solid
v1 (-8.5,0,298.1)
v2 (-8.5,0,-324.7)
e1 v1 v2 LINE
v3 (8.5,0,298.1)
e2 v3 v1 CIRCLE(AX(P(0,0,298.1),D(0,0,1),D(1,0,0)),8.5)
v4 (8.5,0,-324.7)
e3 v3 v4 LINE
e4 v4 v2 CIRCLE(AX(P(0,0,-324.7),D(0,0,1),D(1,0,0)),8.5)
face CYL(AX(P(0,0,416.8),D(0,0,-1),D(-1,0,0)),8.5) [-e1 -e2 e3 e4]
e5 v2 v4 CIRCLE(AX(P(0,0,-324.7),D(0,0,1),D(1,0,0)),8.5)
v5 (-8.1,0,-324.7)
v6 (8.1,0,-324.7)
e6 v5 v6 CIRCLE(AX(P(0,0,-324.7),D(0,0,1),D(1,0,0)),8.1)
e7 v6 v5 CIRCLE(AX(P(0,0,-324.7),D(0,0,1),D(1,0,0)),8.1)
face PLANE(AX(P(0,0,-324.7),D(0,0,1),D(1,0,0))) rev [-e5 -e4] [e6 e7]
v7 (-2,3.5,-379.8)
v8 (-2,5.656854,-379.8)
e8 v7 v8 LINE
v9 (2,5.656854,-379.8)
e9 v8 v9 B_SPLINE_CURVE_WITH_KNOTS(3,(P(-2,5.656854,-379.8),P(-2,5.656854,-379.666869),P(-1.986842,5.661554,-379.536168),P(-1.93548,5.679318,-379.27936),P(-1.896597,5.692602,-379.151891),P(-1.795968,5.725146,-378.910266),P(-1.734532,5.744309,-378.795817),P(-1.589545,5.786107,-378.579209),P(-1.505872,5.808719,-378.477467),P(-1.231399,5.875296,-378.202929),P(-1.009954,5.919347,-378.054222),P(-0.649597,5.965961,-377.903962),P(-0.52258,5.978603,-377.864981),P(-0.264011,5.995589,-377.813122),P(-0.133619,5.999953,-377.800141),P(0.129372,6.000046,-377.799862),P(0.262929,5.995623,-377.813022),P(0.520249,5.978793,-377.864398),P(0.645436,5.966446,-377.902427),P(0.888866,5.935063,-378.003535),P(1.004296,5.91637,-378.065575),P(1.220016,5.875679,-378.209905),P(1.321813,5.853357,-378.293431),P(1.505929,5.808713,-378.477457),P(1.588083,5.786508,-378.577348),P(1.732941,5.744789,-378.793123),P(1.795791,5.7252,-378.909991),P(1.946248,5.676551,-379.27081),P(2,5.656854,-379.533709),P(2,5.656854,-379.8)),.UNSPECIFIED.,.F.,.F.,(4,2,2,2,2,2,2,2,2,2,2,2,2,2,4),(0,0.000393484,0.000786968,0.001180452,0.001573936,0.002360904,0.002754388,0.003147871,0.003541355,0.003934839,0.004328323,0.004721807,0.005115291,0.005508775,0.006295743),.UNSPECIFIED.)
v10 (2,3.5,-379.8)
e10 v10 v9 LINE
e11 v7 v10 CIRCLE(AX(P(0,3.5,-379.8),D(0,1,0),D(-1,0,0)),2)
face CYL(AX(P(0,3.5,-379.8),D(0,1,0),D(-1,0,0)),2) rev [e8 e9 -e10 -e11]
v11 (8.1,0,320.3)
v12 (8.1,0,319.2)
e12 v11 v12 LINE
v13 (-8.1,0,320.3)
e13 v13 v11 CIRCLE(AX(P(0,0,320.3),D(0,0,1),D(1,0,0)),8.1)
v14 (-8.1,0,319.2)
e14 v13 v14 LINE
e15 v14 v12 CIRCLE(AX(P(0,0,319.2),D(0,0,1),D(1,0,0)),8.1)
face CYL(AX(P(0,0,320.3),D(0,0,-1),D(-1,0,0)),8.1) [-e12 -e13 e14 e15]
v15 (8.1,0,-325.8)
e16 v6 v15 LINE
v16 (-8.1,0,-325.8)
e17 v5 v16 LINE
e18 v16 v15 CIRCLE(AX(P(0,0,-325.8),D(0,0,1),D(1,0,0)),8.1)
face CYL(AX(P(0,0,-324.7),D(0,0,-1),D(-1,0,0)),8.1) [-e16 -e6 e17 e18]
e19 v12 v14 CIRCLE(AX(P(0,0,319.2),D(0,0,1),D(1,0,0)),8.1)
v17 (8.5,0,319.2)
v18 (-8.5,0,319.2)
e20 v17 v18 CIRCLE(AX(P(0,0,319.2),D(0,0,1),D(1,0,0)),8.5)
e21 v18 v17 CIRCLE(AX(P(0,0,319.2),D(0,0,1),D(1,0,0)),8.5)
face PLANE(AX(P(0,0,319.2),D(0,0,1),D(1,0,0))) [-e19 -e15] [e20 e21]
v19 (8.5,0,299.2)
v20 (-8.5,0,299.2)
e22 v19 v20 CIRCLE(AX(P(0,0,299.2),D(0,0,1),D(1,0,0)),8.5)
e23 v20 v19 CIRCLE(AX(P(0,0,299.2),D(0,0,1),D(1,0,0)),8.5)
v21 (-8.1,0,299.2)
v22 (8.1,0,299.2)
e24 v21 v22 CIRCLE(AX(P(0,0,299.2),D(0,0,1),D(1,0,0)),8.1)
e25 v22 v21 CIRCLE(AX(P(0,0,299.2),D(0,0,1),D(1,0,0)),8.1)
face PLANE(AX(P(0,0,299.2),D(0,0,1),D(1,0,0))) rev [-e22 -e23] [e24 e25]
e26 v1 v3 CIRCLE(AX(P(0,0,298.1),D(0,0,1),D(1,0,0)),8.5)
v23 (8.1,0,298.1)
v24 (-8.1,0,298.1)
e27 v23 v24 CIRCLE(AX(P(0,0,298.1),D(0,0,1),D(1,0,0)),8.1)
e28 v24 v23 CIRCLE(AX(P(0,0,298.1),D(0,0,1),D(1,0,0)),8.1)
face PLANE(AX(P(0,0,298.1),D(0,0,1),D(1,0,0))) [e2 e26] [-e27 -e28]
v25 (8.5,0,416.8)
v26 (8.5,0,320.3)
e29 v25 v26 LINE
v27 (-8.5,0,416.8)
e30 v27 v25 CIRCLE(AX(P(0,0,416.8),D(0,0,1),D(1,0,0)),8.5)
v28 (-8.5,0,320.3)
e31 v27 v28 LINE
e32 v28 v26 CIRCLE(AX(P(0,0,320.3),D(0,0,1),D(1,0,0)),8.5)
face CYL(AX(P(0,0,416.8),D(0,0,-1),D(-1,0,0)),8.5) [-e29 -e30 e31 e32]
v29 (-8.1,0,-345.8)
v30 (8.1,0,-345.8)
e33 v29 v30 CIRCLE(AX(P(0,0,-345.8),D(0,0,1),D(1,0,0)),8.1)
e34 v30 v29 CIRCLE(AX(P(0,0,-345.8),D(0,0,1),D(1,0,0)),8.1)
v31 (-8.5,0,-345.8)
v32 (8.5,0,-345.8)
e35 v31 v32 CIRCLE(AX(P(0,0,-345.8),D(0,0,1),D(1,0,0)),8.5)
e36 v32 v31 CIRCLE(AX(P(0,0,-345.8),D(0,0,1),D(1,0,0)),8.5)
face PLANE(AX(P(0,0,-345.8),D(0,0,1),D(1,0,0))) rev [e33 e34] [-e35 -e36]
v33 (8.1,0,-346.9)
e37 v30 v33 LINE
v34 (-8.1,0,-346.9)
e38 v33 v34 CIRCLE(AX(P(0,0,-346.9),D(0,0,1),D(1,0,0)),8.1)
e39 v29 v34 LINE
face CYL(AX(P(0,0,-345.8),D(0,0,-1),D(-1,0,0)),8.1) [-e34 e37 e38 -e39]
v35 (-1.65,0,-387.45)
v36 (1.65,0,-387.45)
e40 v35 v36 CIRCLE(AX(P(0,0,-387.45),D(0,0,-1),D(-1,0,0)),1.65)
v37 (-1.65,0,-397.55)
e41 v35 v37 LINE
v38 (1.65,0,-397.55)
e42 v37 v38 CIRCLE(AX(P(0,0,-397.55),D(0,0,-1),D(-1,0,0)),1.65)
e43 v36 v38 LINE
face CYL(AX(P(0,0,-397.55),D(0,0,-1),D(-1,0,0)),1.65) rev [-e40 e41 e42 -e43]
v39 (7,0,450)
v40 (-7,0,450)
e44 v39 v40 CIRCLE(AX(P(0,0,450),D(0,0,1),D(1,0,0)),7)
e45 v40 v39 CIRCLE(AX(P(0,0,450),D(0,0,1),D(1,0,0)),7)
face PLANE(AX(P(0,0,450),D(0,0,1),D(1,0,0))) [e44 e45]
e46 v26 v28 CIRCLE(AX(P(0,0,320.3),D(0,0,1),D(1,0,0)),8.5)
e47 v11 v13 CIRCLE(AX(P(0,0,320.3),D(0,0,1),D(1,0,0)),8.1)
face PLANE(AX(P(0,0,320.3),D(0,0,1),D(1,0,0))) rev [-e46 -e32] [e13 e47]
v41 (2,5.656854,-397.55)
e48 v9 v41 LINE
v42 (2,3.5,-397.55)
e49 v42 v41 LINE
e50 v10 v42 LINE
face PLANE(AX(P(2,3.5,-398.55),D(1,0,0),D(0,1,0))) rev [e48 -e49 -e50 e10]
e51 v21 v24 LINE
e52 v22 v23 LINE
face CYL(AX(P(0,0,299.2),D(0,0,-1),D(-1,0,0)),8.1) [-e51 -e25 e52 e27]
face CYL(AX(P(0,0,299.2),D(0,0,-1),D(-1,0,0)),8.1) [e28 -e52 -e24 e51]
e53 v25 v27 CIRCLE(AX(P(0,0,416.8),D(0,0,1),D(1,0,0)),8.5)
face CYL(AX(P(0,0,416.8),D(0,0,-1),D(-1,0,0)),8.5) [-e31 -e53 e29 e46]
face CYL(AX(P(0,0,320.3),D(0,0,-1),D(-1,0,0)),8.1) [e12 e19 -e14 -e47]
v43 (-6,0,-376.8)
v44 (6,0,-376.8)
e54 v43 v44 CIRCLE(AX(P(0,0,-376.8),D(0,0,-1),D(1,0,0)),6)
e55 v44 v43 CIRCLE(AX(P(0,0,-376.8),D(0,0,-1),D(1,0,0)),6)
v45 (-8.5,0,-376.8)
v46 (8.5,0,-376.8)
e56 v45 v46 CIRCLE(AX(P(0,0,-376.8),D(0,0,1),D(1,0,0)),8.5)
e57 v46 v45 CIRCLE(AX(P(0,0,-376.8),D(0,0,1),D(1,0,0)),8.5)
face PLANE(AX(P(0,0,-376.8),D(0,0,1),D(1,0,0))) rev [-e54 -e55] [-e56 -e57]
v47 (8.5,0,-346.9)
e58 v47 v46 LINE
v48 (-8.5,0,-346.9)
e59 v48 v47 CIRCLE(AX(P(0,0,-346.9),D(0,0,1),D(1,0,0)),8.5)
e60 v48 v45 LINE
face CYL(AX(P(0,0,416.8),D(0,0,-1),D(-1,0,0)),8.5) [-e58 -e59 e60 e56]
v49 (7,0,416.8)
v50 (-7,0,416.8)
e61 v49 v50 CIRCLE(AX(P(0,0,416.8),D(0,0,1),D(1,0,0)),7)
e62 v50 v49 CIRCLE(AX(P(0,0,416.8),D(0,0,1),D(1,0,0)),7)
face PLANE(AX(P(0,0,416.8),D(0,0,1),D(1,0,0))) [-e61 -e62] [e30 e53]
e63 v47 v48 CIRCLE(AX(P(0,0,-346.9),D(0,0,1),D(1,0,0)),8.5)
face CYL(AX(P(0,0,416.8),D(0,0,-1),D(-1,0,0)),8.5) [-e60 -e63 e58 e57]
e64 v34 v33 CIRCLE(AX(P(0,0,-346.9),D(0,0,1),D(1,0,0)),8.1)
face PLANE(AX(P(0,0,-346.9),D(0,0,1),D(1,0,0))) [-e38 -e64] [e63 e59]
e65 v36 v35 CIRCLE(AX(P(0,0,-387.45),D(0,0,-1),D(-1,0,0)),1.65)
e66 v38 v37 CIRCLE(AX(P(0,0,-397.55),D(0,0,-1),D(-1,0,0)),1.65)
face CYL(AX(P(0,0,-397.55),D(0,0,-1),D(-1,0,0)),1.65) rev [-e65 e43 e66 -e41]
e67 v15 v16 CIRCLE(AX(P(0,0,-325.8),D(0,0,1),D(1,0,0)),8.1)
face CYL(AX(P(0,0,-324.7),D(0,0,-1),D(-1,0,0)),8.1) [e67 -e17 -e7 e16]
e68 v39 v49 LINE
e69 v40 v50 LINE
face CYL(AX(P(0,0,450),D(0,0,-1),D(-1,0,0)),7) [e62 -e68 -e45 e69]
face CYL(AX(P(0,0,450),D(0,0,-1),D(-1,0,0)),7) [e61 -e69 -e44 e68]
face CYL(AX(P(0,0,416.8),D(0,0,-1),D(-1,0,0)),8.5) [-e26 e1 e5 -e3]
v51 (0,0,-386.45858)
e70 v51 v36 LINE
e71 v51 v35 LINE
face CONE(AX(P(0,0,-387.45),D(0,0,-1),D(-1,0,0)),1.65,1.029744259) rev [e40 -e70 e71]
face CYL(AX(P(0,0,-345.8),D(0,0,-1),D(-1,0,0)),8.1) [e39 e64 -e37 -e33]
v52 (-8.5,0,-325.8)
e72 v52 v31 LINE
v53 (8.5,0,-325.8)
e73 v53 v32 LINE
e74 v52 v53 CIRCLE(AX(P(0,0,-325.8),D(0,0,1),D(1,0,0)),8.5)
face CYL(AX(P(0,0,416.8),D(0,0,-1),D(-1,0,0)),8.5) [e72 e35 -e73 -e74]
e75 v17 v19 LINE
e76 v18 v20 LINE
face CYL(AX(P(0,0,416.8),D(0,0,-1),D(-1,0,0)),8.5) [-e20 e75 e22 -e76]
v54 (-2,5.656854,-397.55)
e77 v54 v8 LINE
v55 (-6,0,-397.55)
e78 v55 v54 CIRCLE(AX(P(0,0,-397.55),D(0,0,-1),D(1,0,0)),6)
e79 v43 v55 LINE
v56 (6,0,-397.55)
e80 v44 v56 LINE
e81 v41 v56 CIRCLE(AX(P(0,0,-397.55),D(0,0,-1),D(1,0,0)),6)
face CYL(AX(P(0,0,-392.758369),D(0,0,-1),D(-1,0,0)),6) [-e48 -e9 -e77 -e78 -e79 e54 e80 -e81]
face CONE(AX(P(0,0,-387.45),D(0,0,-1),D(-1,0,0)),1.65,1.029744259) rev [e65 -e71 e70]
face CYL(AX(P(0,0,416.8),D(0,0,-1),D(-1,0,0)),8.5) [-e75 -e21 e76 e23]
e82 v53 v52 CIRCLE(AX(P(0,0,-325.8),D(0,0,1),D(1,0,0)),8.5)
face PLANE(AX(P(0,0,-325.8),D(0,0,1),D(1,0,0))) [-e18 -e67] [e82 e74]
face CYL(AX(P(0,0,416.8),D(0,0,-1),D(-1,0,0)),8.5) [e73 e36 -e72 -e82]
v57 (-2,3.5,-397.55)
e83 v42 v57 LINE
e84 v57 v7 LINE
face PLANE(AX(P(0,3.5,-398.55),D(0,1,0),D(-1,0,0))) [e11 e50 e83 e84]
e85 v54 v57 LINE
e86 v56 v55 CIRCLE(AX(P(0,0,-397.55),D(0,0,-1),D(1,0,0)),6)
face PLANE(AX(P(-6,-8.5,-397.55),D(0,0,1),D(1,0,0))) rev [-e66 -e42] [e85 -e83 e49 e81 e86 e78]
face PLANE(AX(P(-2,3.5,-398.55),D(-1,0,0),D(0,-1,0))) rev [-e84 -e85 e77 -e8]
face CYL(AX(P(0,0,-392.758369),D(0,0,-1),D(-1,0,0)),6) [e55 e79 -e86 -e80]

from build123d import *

# Parameters (mm, degrees)
SKETCH_1_R               = 7
EXTRUDE_1_DEPTH          = 450
SKETCH_2_R               = 8.5
EXTRUDE_2_DEPTH          = 416.8
CUT_EXTRUDE_START        = -33.2
SKETCH_3_R               = 8.5
SKETCH_3_R_2             = 6
CUT_EXTRUDE_1_DEPTH      = 33.2
CUT_EXTRUDE_2_DEPTH      = 451.160526923
CUT_EXTRUDE_2_DEPTH_BACK = 451.160526923
SKETCH_4_W               = 12
SKETCH_4_H               = 12.45
MOVE_FACE_1_BY           = 40
MOVE_FACE_1_2_BY         = 40
CUT_EXTRUDE_11_DEPTH     = 2.5
HOLE_WIZARD_M4_1_D       = 3.3
HOLE_WIZARD_M4_1_DEPTH   = 10.1
HOLE_WIZARD_M4_1_TIP     = 0.991420021
CUT_EXTRUDE_START_2      = 1.1
SKETCH_35_R              = 8.5
SKETCH_35_R_2            = 8.1
CUT_EXTRUDE_12_DEPTH     = 1.1
SKETCH_36_R              = 8.5
SKETCH_36_R_2            = 8.1
CUT_EXTRUDE_13_DEPTH     = 1.1
SKETCH_37_R              = 8.5
SKETCH_37_R_2            = 8.1
CUT_EXTRUDE_14_DEPTH     = 1.1
SKETCH_38_R              = 8.5
SKETCH_38_R_2            = 8.1
CUT_EXTRUDE_15_DEPTH     = 1.1


with BuildPart() as part:
    # 草图1 → 凸台-拉伸1 (new, symmetric)
    with BuildSketch(Plane.XY):
        Circle(SKETCH_1_R)
    extrude(amount=EXTRUDE_1_DEPTH, both=True)

    # 草图2 → 凸台-拉伸2 (add, symmetric)
    with BuildSketch(Plane.XY):
        Circle(SKETCH_2_R)
    extrude(amount=EXTRUDE_2_DEPTH, both=True)

    # 草图3 → 切除-拉伸1 (cut)
    with BuildSketch(Plane(origin=(0, 0, -450), x_dir=(-1, 0, 0), z_dir=(0, 0, -1)).offset(CUT_EXTRUDE_START)):
        with Locations(Location((0, 0, 0), (0, 0, 180))):
            Circle(SKETCH_3_R)
        Circle(SKETCH_3_R_2, mode=Mode.SUBTRACT)
    extrude(amount=CUT_EXTRUDE_1_DEPTH, mode=Mode.SUBTRACT)

    # 草图4 → 切除-拉伸2 (cut, two sides: drawn at the far end of the back side and taken through both)
    with BuildSketch(Plane(origin=(0, 0, 0), x_dir=(1, 0, 0), z_dir=(0, 1, 0)).offset(-CUT_EXTRUDE_2_DEPTH_BACK)):
        with Locations((0, 443.775)):
            Rectangle(SKETCH_4_W, SKETCH_4_H)
    extrude(amount=CUT_EXTRUDE_2_DEPTH + CUT_EXTRUDE_2_DEPTH_BACK, mode=Mode.SUBTRACT)

    # Move Face 1: a face moved inward by 40.0
    extrude(part.faces().sort_by_distance((0, 0, -437.55))[0], amount=MOVE_FACE_1_BY, dir=(0, 0, 1), mode=Mode.SUBTRACT)

    # Move Face 1 2: a face moved inward by 40.0
    extrude(part.faces().sort_by_distance((0, -6.8, -416.8))[0], amount=MOVE_FACE_1_2_BY, dir=(0, 0, 1), mode=Mode.SUBTRACT)

    # 草图31 → 切除-拉伸11 (cut)
    with BuildSketch(Plane(origin=(0, 6, -397.55), x_dir=(0, 0, 1), z_dir=(0, 1, 0))):
        with BuildLine():
            Line((-1, 2), (17.75, 2))
            ThreePointArc((17.75, 2), (19.75, 0), (17.75, -2))
            Line((17.75, -2), (-1, -2))
            ThreePointArc((-1, -2), (-3, 0), (-1, 2))
        make_face()
    extrude(amount=-CUT_EXTRUDE_11_DEPTH, mode=Mode.SUBTRACT)

    # M4 螺纹孔1
    with Locations(Plane(origin=(0, 0, -397.55), x_dir=(-1, 0, 0), z_dir=(0, 0, -1))):
        with Locations((0, 0)):
            Hole(HOLE_WIZARD_M4_1_D / 2, depth=HOLE_WIZARD_M4_1_DEPTH)
            with Locations((0, 0, -(HOLE_WIZARD_M4_1_DEPTH + HOLE_WIZARD_M4_1_TIP / 2))):  # 118° drill point
                Cone(0, HOLE_WIZARD_M4_1_D / 2, HOLE_WIZARD_M4_1_TIP, mode=Mode.SUBTRACT)

    # 草图35 → 切除-拉伸12 (cut)
    with BuildSketch(Plane.XY.offset(319.2).offset(CUT_EXTRUDE_START_2)):
        Circle(SKETCH_35_R)
        Circle(SKETCH_35_R_2, mode=Mode.SUBTRACT)
    extrude(amount=-CUT_EXTRUDE_12_DEPTH, mode=Mode.SUBTRACT)

    # 草图36 → 切除-拉伸13 (cut)
    with BuildSketch(Plane.XY.offset(298.1).offset(CUT_EXTRUDE_START_2)):
        Circle(SKETCH_36_R)
        Circle(SKETCH_36_R_2, mode=Mode.SUBTRACT)
    extrude(amount=-CUT_EXTRUDE_13_DEPTH, mode=Mode.SUBTRACT)

    # 草图37 → 切除-拉伸14 (cut)
    with BuildSketch(Plane.XY.offset(-325.8).offset(CUT_EXTRUDE_START_2)):
        Circle(SKETCH_37_R)
        Circle(SKETCH_37_R_2, mode=Mode.SUBTRACT)
    extrude(amount=-CUT_EXTRUDE_14_DEPTH, mode=Mode.SUBTRACT)

    # 草图38 → 切除-拉伸15 (cut)
    with BuildSketch(Plane.XY.offset(-346.9).offset(CUT_EXTRUDE_START_2)):
        Circle(SKETCH_38_R)
        Circle(SKETCH_38_R_2, mode=Mode.SUBTRACT)
    extrude(amount=-CUT_EXTRUDE_15_DEPTH, mode=Mode.SUBTRACT)


solid = part.part
